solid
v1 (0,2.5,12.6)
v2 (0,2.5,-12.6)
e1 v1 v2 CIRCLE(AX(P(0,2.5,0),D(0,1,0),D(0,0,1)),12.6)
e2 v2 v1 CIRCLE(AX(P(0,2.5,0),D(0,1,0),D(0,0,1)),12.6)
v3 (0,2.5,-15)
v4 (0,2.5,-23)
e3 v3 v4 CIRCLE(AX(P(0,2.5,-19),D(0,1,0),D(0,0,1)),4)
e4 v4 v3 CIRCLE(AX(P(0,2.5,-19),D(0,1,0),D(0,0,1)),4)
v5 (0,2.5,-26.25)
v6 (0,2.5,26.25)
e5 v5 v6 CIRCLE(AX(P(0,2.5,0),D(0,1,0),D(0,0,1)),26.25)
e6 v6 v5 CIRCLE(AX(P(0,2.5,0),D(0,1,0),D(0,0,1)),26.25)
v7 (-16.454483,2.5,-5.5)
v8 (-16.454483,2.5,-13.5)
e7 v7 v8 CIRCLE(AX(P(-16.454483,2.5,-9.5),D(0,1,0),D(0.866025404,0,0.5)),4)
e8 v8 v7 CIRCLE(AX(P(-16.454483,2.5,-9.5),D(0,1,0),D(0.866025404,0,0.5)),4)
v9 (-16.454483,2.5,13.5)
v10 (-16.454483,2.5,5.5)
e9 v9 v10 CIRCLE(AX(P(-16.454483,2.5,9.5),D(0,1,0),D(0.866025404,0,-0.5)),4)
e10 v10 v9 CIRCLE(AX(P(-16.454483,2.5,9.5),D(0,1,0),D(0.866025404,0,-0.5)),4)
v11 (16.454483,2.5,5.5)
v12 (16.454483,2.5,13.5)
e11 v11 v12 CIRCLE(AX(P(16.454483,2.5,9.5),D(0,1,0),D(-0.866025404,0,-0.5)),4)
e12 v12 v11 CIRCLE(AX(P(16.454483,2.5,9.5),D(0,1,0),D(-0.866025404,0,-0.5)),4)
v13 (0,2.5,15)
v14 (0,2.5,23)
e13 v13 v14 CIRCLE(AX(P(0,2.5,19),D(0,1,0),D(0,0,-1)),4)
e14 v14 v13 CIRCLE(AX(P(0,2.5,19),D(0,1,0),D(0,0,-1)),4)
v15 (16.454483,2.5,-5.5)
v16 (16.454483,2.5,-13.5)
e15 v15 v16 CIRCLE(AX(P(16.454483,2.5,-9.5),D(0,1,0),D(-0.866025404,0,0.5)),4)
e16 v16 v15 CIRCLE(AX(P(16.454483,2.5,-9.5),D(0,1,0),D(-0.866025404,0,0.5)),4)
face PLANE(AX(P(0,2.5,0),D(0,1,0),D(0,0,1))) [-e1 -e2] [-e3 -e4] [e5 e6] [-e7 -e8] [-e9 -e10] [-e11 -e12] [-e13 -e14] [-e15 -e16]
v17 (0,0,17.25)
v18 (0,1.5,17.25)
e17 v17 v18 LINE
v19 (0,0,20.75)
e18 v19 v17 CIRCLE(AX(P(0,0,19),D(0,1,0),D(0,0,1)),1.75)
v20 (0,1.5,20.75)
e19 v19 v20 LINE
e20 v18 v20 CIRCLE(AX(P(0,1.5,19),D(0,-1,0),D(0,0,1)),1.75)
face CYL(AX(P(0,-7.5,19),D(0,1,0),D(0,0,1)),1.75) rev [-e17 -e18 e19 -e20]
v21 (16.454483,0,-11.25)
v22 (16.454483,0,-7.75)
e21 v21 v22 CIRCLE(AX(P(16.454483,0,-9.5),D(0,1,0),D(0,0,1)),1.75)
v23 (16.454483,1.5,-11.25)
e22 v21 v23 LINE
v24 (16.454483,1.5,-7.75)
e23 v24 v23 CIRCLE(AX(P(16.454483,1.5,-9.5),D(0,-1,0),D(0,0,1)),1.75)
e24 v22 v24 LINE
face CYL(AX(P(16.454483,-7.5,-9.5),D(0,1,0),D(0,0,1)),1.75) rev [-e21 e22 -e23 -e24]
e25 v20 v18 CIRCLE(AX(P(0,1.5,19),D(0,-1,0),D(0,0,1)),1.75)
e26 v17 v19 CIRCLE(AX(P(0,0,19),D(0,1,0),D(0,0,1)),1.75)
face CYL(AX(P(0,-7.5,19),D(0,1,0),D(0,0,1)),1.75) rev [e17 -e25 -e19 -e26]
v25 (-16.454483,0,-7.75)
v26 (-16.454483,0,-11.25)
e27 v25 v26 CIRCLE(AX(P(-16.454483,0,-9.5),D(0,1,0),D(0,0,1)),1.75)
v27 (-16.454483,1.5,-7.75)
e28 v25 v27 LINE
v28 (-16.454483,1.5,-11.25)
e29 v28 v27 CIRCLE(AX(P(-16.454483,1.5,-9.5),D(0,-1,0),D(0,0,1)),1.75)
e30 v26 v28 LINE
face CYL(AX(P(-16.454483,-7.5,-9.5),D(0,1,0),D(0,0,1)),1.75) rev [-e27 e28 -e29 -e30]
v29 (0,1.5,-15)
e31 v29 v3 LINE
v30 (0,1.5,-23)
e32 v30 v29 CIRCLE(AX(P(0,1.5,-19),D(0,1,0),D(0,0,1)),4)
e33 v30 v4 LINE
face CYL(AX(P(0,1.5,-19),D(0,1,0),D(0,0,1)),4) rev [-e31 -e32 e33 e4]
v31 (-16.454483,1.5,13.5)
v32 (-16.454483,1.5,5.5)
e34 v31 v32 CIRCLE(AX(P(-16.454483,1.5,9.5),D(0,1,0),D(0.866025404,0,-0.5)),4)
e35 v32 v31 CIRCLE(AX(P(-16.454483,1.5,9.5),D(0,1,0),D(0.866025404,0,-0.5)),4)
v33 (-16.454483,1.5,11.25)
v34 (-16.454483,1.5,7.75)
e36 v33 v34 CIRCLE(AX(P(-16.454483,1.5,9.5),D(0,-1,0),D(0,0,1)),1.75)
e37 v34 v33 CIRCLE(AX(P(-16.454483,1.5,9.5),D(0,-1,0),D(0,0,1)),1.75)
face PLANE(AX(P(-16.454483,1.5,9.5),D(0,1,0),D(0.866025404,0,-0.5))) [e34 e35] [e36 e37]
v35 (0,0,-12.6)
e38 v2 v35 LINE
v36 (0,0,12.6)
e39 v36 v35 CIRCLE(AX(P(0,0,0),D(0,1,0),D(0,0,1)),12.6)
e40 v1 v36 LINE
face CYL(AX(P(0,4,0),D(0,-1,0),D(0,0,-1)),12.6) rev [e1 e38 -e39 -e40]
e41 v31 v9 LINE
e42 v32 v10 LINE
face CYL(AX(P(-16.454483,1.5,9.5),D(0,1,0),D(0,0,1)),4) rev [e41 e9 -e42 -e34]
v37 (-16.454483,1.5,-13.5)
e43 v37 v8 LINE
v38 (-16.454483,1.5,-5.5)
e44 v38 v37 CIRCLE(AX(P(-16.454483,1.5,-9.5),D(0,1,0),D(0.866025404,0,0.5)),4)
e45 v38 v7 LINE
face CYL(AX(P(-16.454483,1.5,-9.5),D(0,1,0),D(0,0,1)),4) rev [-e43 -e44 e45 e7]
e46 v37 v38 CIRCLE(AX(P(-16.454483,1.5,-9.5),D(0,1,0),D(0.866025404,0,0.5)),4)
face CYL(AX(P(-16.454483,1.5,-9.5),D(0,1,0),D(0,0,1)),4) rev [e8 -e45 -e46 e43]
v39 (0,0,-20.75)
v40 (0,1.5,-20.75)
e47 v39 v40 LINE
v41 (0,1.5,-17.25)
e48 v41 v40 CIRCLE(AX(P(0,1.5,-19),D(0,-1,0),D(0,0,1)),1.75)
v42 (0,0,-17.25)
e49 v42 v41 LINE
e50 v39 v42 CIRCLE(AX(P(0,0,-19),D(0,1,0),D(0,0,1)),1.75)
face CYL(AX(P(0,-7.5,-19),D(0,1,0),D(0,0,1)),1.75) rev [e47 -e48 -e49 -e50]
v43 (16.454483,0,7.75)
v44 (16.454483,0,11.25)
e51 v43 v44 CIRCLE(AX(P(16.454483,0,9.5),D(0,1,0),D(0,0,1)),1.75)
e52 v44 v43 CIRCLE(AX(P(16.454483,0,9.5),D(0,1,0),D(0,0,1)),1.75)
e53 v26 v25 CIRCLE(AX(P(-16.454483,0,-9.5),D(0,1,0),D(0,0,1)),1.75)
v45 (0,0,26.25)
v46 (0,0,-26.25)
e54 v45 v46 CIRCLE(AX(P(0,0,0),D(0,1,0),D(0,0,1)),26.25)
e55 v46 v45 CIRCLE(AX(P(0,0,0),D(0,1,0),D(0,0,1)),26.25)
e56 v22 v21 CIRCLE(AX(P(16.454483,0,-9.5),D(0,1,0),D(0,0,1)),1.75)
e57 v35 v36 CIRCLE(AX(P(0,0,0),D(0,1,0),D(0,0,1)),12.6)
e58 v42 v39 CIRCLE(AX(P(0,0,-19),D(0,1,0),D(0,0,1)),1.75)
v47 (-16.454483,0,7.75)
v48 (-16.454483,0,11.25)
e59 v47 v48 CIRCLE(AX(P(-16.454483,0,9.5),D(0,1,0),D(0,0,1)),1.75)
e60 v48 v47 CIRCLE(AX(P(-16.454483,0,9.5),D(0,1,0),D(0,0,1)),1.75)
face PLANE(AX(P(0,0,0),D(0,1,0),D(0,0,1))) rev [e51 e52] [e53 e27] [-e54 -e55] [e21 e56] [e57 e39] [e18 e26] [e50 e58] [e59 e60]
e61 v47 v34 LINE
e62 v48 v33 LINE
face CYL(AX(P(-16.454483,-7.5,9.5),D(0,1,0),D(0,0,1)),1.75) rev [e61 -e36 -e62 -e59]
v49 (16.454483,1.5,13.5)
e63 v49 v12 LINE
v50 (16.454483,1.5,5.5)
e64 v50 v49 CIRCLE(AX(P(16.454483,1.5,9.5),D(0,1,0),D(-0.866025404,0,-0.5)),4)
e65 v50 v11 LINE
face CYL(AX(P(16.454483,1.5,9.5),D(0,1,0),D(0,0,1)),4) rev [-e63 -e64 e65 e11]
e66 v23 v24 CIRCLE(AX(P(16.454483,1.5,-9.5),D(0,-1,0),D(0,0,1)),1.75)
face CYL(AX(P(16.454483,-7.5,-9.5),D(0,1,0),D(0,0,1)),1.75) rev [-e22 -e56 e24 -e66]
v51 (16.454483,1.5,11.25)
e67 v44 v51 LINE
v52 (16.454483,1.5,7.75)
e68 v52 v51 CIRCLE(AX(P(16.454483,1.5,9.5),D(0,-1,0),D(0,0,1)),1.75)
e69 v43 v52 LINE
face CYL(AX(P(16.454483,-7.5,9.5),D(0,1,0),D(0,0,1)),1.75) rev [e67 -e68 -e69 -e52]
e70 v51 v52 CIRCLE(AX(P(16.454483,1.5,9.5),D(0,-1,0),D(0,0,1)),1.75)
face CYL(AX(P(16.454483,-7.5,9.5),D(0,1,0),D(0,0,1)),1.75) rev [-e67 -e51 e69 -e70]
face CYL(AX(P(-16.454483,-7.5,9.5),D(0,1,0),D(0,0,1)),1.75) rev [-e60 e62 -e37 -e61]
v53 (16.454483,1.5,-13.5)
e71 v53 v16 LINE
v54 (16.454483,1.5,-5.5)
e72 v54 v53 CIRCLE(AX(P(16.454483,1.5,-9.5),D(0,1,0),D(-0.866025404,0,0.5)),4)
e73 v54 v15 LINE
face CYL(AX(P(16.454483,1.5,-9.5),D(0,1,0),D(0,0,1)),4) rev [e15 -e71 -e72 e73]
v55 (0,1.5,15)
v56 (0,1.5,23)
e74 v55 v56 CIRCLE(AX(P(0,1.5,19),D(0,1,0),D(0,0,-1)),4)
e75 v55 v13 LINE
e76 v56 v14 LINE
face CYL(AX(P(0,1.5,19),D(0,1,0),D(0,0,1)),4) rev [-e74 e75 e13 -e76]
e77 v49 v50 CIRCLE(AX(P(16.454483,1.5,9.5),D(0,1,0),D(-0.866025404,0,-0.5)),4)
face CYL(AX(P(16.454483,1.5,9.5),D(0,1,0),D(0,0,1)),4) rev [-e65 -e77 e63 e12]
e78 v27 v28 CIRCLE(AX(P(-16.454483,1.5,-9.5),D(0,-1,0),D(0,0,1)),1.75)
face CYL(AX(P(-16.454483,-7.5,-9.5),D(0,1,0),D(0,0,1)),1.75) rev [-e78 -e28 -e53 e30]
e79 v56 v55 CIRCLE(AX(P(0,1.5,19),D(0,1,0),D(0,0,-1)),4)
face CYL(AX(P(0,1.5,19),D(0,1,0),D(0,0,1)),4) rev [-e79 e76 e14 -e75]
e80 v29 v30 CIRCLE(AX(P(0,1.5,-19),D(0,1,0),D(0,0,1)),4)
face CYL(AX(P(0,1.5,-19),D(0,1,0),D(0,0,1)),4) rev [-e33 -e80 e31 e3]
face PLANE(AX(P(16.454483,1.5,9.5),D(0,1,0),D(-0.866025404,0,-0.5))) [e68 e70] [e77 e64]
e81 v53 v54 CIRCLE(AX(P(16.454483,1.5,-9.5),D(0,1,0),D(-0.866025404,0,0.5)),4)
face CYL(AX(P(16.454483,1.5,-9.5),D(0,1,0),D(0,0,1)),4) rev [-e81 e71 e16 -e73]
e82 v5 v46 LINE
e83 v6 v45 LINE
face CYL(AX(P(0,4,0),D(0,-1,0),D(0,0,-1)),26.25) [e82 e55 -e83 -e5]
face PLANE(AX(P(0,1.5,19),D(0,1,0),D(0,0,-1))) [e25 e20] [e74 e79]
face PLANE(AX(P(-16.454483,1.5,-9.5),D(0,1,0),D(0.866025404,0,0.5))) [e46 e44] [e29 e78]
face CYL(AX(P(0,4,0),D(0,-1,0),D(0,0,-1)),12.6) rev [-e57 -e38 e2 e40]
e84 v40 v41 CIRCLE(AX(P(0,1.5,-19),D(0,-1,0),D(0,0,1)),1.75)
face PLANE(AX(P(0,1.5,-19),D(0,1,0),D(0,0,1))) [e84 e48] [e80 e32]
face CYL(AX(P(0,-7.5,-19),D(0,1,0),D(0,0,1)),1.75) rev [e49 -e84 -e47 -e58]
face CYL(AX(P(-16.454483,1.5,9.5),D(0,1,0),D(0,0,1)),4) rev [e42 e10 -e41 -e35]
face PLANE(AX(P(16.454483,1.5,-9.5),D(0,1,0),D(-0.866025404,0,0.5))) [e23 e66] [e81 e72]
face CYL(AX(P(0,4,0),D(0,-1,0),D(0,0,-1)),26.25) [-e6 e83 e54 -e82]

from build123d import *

# Parameters (mm, degrees)
SKETCH1_R           = 26.25
SKETCH1_R_2         = 12.6
BOSS_EXTRUDE1_DEPTH = 4
SKETCH2_R           = 35
SKETCH2_R_2         = 14.25
CUT_EXTRUDE1_DEPTH  = 1.5
SKETCH4_R           = 1.75
CUT_EXTRUDE2_DEPTH  = 10
CIRPATTERN1_COUNT   = 6
SKETCH5_R           = 4
CUT_EXTRUDE3_DEPTH  = 1
CIRPATTERN2_COUNT   = 6
CHAMFER1_SIZE       = 0.5
SKETCH6_R           = 14.25
CUT_EXTRUDE4_DEPTH  = 1.5


with BuildPart() as part:
    # Sketch1 → Boss-Extrude1 (new body)
    with BuildSketch(Plane(origin=(0, 0, 0), x_dir=(1, 0, 0), z_dir=(0, 1, 0))):
        with Locations(Location((0, 0, 0), (0, 0, 270))):
            Circle(SKETCH1_R)
        with Locations(Location((0, 0, 0), (0, 0, 270))):
            Circle(SKETCH1_R_2, mode=Mode.SUBTRACT)
    extrude(amount=BOSS_EXTRUDE1_DEPTH)

    # Sketch2 → Cut-Extrude1 (cut)
    with BuildSketch(Plane(origin=(0, 4, 0), x_dir=(1, 0, 0), z_dir=(0, 1, 0))):
        Circle(SKETCH2_R)
        with Locations(Location((0, 0, 0), (0, 0, 270))):
            Circle(SKETCH2_R_2, mode=Mode.SUBTRACT)
    extrude(amount=-CUT_EXTRUDE1_DEPTH, mode=Mode.SUBTRACT)

    # Sketch4 → Cut-Extrude2 (cut)
    with BuildSketch(Plane(origin=(0, 2.5, 0), x_dir=(1, 0, 0), z_dir=(0, 1, 0))):
        with Locations(Location((0, 19, 0), (0, 0, 270))):
            Circle(SKETCH4_R)
    cut_extrude2 = extrude(amount=-CUT_EXTRUDE2_DEPTH, mode=Mode.SUBTRACT)

    # CirPattern1: Cut-Extrude2 ×6 about axis
    cirpattern1_axis = Axis((0, 0, 0), (0, 1, 0))
    for i in range(1, CIRPATTERN1_COUNT):
        add(cut_extrude2.rotate(cirpattern1_axis, i * 360 / CIRPATTERN1_COUNT), mode=Mode.SUBTRACT)

    # Sketch5 → Cut-Extrude3 (cut)
    with BuildSketch(Plane(origin=(0, 2.5, 0), x_dir=(1, 0, 0), z_dir=(0, 1, 0))):
        with Locations(Location((0, 19, 0), (0, 0, 270))):
            Circle(SKETCH5_R)
    cut_extrude3 = extrude(amount=-CUT_EXTRUDE3_DEPTH, mode=Mode.SUBTRACT)

    # CirPattern2: Cut-Extrude3 ×6 about axis
    cirpattern2_axis = Axis((0, 0, 0), (0, 1, 0))
    for i in range(1, CIRPATTERN2_COUNT):
        add(cut_extrude3.rotate(cirpattern2_axis, i * 360 / CIRPATTERN2_COUNT), mode=Mode.SUBTRACT)

    # Chamfer1
    chamfer1_edges = [part.edges().sort_by_distance(p)[0] for p in [
        (0, 4, -14.25),
    ]]
    chamfer(chamfer1_edges, length=CHAMFER1_SIZE)

    # Sketch6 → Cut-Extrude4 (cut)
    with BuildSketch(Plane(origin=(0, 4, 0), x_dir=(1, 0, 0), z_dir=(0, 1, 0))):
        Circle(SKETCH6_R)
    extrude(amount=-CUT_EXTRUDE4_DEPTH, mode=Mode.SUBTRACT)


solid = part.part
